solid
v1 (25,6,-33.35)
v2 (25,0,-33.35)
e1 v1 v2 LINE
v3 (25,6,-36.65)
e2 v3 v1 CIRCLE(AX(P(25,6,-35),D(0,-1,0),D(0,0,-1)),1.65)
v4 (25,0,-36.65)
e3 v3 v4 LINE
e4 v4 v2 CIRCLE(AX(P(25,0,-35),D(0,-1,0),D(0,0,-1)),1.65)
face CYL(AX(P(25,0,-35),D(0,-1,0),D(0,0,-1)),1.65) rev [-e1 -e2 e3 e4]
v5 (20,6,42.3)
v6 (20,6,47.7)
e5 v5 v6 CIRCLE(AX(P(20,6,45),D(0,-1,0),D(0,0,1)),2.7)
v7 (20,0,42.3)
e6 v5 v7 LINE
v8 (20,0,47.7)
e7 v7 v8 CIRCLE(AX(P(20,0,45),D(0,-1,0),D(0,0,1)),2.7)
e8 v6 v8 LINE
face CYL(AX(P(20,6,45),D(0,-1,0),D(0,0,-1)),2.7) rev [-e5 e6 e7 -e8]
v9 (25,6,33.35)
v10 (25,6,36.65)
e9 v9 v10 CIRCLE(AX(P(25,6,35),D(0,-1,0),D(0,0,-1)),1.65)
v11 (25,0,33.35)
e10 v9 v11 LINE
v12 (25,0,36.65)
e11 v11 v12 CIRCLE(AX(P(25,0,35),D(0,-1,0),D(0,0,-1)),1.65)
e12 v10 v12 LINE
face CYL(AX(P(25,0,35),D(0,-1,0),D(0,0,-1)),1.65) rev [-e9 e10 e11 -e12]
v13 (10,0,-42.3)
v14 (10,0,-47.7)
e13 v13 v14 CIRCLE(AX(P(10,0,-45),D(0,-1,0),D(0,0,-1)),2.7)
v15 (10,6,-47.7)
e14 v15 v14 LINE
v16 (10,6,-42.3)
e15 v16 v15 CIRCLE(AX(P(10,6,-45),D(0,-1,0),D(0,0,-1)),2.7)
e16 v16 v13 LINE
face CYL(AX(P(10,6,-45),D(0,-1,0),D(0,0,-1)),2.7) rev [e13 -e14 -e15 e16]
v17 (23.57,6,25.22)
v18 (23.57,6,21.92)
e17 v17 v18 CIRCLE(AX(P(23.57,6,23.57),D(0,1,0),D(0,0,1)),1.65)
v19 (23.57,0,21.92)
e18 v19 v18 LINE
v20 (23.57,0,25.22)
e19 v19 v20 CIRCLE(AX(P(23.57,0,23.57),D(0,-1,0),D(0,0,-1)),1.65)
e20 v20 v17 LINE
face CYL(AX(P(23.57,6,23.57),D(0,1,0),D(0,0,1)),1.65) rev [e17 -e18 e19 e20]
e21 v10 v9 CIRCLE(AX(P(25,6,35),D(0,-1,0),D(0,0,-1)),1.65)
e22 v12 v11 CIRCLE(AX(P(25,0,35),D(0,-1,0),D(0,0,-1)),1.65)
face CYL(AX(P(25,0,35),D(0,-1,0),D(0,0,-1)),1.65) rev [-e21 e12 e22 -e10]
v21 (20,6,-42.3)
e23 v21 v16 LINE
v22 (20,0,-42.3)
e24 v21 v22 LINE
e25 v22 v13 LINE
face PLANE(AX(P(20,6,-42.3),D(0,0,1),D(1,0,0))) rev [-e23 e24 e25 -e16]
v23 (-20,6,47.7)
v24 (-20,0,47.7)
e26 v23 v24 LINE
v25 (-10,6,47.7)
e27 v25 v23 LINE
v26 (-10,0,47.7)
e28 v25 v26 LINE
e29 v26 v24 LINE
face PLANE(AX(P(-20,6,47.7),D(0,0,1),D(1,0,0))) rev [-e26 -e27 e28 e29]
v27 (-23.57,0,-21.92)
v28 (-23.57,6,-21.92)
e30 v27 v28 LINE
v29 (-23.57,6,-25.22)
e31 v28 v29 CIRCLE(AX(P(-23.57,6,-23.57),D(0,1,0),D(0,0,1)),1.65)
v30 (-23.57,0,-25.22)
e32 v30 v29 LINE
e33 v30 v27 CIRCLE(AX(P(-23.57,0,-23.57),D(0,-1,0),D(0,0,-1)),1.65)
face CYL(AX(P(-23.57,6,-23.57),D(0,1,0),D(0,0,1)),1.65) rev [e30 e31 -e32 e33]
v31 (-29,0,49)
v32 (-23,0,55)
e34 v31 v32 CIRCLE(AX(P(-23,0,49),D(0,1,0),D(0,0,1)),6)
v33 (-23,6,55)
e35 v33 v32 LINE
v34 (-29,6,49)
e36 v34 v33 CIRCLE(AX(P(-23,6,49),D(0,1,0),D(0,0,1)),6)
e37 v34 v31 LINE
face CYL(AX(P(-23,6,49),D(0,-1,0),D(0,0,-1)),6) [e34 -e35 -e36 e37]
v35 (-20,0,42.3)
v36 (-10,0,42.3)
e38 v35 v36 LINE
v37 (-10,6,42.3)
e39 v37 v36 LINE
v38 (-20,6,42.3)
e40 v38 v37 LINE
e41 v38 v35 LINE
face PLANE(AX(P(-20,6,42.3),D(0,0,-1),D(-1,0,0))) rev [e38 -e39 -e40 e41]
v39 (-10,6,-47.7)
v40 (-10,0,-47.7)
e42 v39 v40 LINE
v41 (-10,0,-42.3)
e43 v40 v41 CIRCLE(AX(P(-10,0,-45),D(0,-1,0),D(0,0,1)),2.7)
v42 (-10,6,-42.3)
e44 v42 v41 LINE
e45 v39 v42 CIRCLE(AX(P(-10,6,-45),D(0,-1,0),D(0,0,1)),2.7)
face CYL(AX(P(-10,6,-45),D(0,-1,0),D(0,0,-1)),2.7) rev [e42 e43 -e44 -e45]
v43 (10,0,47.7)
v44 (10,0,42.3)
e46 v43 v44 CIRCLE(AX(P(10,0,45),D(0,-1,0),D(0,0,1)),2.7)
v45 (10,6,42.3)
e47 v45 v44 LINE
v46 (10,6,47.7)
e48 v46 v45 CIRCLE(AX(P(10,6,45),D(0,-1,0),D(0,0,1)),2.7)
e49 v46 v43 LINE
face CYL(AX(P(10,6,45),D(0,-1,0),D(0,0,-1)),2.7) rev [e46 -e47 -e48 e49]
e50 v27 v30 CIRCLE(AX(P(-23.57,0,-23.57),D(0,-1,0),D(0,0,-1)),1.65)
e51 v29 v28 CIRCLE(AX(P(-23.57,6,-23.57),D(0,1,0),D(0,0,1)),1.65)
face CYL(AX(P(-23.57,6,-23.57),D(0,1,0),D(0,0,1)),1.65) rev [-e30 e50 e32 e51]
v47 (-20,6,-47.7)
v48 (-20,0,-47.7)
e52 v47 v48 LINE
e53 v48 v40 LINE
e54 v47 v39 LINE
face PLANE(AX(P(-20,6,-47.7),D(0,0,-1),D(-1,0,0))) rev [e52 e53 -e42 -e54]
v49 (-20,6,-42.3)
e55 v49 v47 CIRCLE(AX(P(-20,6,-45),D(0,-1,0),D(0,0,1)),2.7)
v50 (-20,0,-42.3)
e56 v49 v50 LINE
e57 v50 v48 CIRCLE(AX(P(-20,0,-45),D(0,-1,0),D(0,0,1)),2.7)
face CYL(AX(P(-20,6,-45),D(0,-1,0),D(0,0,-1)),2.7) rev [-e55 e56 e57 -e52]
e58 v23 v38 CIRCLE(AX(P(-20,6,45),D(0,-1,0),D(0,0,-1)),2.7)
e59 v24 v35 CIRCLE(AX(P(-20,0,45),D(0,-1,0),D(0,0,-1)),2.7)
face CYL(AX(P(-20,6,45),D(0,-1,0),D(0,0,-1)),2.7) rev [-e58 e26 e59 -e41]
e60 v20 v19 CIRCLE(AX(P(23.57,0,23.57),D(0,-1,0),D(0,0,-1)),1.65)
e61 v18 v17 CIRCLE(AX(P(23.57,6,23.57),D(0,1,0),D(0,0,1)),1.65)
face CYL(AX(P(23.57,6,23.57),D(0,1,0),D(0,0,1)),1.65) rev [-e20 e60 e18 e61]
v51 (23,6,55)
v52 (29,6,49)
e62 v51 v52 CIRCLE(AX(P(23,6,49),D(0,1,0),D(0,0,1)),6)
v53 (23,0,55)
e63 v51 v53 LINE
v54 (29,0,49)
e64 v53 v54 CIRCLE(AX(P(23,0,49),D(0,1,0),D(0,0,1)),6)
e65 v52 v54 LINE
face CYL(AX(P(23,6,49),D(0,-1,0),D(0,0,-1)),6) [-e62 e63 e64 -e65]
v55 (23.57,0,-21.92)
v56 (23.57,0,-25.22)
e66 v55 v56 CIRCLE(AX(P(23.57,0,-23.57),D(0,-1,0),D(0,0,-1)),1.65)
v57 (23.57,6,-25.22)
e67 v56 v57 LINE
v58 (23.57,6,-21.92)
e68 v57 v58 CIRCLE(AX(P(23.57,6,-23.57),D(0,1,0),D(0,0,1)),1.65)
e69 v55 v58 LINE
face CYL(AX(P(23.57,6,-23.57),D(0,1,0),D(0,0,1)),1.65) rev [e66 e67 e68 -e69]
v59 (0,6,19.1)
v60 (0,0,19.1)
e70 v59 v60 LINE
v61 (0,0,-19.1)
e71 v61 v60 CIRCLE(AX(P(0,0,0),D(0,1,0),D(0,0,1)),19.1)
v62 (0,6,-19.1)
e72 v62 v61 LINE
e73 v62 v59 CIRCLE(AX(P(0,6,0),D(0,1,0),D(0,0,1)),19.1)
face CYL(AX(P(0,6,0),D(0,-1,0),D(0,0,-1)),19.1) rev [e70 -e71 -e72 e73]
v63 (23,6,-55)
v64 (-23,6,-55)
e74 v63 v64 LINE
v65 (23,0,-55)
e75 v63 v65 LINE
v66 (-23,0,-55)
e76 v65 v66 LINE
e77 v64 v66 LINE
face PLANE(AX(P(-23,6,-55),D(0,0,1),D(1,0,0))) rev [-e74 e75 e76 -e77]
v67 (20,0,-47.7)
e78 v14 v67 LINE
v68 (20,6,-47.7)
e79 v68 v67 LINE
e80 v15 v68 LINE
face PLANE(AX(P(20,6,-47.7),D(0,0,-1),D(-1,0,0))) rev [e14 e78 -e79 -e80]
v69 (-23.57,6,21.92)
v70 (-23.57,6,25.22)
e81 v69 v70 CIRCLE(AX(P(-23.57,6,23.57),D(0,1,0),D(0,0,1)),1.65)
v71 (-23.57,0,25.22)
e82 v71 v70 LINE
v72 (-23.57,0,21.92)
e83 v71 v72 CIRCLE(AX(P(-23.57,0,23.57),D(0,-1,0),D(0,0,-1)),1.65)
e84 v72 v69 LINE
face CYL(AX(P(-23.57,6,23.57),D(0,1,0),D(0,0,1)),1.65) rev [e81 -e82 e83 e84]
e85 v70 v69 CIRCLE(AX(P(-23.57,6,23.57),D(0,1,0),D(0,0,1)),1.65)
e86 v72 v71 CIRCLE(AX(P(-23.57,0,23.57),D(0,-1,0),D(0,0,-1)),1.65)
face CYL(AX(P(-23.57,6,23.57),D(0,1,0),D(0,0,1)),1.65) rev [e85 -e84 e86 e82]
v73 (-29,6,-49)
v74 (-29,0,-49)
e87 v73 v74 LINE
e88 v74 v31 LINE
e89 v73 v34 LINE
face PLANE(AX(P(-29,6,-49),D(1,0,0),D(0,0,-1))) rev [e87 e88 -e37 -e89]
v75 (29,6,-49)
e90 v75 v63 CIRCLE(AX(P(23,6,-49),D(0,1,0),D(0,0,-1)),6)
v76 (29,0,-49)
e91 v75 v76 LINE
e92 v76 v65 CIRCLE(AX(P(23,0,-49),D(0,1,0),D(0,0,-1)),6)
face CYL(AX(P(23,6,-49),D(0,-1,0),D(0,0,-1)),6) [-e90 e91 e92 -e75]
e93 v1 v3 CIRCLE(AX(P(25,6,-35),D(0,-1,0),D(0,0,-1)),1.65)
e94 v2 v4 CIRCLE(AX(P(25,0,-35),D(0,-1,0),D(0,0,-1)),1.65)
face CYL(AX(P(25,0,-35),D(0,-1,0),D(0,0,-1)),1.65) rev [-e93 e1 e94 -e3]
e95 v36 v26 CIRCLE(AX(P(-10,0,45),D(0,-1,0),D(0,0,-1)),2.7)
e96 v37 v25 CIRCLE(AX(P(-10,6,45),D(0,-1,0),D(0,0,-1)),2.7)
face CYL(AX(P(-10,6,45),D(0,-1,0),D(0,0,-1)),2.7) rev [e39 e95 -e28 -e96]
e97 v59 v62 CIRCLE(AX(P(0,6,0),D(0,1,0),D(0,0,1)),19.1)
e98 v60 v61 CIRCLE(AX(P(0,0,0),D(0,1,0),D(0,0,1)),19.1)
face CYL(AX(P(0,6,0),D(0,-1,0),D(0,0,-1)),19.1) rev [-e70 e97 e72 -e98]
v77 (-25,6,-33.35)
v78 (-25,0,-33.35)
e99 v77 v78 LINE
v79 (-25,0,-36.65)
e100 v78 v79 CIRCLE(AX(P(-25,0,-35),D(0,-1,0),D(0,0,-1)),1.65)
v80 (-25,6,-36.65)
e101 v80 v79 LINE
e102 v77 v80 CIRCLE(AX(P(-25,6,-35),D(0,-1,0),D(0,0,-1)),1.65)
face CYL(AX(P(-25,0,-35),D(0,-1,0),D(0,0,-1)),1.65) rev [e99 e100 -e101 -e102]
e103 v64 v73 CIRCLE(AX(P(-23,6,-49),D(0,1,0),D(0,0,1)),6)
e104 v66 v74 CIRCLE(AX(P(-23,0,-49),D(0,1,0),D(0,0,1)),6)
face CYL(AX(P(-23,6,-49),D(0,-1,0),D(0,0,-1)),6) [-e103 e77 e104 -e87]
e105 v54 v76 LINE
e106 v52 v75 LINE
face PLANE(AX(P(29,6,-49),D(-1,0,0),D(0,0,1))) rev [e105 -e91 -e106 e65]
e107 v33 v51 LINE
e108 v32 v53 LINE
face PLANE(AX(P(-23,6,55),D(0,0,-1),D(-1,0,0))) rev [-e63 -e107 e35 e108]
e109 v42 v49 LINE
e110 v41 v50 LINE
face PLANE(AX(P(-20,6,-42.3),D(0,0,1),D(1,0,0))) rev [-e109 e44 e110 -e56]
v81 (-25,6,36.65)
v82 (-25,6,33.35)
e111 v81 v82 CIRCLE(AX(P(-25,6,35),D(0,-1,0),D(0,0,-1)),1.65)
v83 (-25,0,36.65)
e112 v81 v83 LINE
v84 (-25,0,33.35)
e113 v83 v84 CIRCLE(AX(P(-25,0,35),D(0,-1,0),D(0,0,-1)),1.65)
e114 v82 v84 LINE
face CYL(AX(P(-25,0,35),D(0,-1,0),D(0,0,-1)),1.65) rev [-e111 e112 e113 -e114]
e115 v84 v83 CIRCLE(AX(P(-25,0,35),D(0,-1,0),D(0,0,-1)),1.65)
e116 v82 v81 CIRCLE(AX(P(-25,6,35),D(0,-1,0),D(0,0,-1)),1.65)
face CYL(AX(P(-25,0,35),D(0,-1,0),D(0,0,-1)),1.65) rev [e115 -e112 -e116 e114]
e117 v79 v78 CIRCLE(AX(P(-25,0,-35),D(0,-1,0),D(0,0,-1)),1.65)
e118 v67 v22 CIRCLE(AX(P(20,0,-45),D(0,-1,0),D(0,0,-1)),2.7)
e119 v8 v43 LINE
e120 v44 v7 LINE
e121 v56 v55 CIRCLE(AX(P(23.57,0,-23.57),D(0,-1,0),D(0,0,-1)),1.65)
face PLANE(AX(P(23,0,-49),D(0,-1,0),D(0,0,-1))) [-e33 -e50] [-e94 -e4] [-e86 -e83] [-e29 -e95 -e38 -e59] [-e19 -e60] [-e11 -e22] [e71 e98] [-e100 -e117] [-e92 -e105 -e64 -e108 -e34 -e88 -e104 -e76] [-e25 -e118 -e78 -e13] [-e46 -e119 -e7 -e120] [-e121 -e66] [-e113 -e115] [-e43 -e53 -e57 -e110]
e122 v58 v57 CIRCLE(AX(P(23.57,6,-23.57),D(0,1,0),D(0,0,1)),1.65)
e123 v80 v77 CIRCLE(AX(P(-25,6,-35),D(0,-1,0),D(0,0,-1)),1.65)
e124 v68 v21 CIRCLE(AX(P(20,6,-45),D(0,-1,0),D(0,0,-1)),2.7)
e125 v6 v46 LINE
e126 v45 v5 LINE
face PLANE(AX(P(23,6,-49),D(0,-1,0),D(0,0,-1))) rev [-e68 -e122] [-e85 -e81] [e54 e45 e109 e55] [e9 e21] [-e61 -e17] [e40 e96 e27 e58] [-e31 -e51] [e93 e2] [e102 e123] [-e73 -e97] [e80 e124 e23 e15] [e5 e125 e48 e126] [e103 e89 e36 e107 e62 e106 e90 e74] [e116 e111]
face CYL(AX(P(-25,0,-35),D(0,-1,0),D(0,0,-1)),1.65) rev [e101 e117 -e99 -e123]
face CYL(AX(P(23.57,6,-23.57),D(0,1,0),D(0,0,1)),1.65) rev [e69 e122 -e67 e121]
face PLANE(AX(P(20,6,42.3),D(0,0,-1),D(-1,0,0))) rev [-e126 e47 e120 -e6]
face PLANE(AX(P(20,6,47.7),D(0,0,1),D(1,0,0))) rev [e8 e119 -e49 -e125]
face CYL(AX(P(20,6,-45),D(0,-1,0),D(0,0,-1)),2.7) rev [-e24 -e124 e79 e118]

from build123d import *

# Parameters (mm, degrees)
SKETCH1_R             = 19.1
BOSS_EXTRUDE1_DEPTH   = 6
M4_TAPPED_HOLE1_D     = 3.3
M4_TAPPED_HOLE1_DEPTH = 10.1
M4_TAPPED_HOLE1_TIP   = 0.991420021
CUT_EXTRUDE1_DEPTH    = 63.465990747
M4_TAPPED_HOLE2_D     = 3.3
M4_TAPPED_HOLE2_DEPTH = 10.1
M4_TAPPED_HOLE2_TIP   = 0.991420021


with BuildPart() as part:
    # Sketch1 → Boss-Extrude1 (new body)
    with BuildSketch(Plane(origin=(0, 0, 0), x_dir=(1, 0, 0), z_dir=(0, 1, 0))):
        with BuildLine():
            Line((-23, 55), (23, 55))
            ThreePointArc((23, 55), (27.242640687, 53.242640687), (29, 49))
            Line((29, 49), (29, -49))
            ThreePointArc((29, -49), (27.242640687, -53.242640687), (23, -55))
            Line((23, -55), (-23, -55))
            ThreePointArc((-23, -55), (-27.242640687, -53.242640687), (-29, -49))
            Line((-29, -49), (-29, 49))
            ThreePointArc((-29, 49), (-27.242640687, 53.242640687), (-23, 55))
        make_face()
        with Locations(Location((0, 0, 0), (0, 0, 270))):
            Circle(SKETCH1_R, mode=Mode.SUBTRACT)
    extrude(amount=BOSS_EXTRUDE1_DEPTH)

    # M4 Tapped Hole1
    with Locations(Plane(origin=(0, 6, 0), x_dir=(1, 0, 0), z_dir=(0, 1, 0))):
        with Locations((-23.57, 23.57), (23.57, 23.57), (23.57, -23.57), (-23.57, -23.57)):
            Hole(M4_TAPPED_HOLE1_D / 2, depth=M4_TAPPED_HOLE1_DEPTH)
            with Locations((0, 0, -(M4_TAPPED_HOLE1_DEPTH + M4_TAPPED_HOLE1_TIP / 2))):  # 118° drill point
                Cone(0, M4_TAPPED_HOLE1_D / 2, M4_TAPPED_HOLE1_TIP, mode=Mode.SUBTRACT)

    # Sketch4 → Cut-Extrude1 (cut, through all)
    with BuildSketch(Plane.XZ):
        with BuildLine():
            Line((-20, 47.7), (-10, 47.7))
            ThreePointArc((-10, 47.7), (-7.3, 45), (-10, 42.3))
            Line((-10, 42.3), (-20, 42.3))
            ThreePointArc((-20, 42.3), (-22.7, 45), (-20, 47.7))
        make_face()
        with BuildLine():
            Line((20, 47.7), (10, 47.7))
            ThreePointArc((10, 47.7), (7.3, 45), (10, 42.3))
            Line((10, 42.3), (20, 42.3))
            ThreePointArc((20, 42.3), (22.7, 45), (20, 47.7))
        make_face()
        with BuildLine():
            Line((-20, -47.7), (-10, -47.7))
            ThreePointArc((-10, -47.7), (-7.3, -45), (-10, -42.3))
            Line((-10, -42.3), (-20, -42.3))
            ThreePointArc((-20, -42.3), (-22.7, -45), (-20, -47.7))
        make_face()
        with BuildLine():
            Line((20, -47.7), (10, -47.7))
            ThreePointArc((10, -47.7), (7.3, -45), (10, -42.3))
            Line((10, -42.3), (20, -42.3))
            ThreePointArc((20, -42.3), (22.7, -45), (20, -47.7))
        make_face()
    extrude(amount=-CUT_EXTRUDE1_DEPTH, mode=Mode.SUBTRACT)

    # M4 Tapped Hole2
    with Locations(Plane(origin=(0, 0, 0), x_dir=(-1, 0, 0), z_dir=(0, -1, 0))):
        with Locations((25, -35), (25, 35), (-25, 35), (-25, -35)):
            Hole(M4_TAPPED_HOLE2_D / 2, depth=M4_TAPPED_HOLE2_DEPTH)
            with Locations((0, 0, -(M4_TAPPED_HOLE2_DEPTH + M4_TAPPED_HOLE2_TIP / 2))):  # 118° drill point
                Cone(0, M4_TAPPED_HOLE2_D / 2, M4_TAPPED_HOLE2_TIP, mode=Mode.SUBTRACT)


solid = part.part
